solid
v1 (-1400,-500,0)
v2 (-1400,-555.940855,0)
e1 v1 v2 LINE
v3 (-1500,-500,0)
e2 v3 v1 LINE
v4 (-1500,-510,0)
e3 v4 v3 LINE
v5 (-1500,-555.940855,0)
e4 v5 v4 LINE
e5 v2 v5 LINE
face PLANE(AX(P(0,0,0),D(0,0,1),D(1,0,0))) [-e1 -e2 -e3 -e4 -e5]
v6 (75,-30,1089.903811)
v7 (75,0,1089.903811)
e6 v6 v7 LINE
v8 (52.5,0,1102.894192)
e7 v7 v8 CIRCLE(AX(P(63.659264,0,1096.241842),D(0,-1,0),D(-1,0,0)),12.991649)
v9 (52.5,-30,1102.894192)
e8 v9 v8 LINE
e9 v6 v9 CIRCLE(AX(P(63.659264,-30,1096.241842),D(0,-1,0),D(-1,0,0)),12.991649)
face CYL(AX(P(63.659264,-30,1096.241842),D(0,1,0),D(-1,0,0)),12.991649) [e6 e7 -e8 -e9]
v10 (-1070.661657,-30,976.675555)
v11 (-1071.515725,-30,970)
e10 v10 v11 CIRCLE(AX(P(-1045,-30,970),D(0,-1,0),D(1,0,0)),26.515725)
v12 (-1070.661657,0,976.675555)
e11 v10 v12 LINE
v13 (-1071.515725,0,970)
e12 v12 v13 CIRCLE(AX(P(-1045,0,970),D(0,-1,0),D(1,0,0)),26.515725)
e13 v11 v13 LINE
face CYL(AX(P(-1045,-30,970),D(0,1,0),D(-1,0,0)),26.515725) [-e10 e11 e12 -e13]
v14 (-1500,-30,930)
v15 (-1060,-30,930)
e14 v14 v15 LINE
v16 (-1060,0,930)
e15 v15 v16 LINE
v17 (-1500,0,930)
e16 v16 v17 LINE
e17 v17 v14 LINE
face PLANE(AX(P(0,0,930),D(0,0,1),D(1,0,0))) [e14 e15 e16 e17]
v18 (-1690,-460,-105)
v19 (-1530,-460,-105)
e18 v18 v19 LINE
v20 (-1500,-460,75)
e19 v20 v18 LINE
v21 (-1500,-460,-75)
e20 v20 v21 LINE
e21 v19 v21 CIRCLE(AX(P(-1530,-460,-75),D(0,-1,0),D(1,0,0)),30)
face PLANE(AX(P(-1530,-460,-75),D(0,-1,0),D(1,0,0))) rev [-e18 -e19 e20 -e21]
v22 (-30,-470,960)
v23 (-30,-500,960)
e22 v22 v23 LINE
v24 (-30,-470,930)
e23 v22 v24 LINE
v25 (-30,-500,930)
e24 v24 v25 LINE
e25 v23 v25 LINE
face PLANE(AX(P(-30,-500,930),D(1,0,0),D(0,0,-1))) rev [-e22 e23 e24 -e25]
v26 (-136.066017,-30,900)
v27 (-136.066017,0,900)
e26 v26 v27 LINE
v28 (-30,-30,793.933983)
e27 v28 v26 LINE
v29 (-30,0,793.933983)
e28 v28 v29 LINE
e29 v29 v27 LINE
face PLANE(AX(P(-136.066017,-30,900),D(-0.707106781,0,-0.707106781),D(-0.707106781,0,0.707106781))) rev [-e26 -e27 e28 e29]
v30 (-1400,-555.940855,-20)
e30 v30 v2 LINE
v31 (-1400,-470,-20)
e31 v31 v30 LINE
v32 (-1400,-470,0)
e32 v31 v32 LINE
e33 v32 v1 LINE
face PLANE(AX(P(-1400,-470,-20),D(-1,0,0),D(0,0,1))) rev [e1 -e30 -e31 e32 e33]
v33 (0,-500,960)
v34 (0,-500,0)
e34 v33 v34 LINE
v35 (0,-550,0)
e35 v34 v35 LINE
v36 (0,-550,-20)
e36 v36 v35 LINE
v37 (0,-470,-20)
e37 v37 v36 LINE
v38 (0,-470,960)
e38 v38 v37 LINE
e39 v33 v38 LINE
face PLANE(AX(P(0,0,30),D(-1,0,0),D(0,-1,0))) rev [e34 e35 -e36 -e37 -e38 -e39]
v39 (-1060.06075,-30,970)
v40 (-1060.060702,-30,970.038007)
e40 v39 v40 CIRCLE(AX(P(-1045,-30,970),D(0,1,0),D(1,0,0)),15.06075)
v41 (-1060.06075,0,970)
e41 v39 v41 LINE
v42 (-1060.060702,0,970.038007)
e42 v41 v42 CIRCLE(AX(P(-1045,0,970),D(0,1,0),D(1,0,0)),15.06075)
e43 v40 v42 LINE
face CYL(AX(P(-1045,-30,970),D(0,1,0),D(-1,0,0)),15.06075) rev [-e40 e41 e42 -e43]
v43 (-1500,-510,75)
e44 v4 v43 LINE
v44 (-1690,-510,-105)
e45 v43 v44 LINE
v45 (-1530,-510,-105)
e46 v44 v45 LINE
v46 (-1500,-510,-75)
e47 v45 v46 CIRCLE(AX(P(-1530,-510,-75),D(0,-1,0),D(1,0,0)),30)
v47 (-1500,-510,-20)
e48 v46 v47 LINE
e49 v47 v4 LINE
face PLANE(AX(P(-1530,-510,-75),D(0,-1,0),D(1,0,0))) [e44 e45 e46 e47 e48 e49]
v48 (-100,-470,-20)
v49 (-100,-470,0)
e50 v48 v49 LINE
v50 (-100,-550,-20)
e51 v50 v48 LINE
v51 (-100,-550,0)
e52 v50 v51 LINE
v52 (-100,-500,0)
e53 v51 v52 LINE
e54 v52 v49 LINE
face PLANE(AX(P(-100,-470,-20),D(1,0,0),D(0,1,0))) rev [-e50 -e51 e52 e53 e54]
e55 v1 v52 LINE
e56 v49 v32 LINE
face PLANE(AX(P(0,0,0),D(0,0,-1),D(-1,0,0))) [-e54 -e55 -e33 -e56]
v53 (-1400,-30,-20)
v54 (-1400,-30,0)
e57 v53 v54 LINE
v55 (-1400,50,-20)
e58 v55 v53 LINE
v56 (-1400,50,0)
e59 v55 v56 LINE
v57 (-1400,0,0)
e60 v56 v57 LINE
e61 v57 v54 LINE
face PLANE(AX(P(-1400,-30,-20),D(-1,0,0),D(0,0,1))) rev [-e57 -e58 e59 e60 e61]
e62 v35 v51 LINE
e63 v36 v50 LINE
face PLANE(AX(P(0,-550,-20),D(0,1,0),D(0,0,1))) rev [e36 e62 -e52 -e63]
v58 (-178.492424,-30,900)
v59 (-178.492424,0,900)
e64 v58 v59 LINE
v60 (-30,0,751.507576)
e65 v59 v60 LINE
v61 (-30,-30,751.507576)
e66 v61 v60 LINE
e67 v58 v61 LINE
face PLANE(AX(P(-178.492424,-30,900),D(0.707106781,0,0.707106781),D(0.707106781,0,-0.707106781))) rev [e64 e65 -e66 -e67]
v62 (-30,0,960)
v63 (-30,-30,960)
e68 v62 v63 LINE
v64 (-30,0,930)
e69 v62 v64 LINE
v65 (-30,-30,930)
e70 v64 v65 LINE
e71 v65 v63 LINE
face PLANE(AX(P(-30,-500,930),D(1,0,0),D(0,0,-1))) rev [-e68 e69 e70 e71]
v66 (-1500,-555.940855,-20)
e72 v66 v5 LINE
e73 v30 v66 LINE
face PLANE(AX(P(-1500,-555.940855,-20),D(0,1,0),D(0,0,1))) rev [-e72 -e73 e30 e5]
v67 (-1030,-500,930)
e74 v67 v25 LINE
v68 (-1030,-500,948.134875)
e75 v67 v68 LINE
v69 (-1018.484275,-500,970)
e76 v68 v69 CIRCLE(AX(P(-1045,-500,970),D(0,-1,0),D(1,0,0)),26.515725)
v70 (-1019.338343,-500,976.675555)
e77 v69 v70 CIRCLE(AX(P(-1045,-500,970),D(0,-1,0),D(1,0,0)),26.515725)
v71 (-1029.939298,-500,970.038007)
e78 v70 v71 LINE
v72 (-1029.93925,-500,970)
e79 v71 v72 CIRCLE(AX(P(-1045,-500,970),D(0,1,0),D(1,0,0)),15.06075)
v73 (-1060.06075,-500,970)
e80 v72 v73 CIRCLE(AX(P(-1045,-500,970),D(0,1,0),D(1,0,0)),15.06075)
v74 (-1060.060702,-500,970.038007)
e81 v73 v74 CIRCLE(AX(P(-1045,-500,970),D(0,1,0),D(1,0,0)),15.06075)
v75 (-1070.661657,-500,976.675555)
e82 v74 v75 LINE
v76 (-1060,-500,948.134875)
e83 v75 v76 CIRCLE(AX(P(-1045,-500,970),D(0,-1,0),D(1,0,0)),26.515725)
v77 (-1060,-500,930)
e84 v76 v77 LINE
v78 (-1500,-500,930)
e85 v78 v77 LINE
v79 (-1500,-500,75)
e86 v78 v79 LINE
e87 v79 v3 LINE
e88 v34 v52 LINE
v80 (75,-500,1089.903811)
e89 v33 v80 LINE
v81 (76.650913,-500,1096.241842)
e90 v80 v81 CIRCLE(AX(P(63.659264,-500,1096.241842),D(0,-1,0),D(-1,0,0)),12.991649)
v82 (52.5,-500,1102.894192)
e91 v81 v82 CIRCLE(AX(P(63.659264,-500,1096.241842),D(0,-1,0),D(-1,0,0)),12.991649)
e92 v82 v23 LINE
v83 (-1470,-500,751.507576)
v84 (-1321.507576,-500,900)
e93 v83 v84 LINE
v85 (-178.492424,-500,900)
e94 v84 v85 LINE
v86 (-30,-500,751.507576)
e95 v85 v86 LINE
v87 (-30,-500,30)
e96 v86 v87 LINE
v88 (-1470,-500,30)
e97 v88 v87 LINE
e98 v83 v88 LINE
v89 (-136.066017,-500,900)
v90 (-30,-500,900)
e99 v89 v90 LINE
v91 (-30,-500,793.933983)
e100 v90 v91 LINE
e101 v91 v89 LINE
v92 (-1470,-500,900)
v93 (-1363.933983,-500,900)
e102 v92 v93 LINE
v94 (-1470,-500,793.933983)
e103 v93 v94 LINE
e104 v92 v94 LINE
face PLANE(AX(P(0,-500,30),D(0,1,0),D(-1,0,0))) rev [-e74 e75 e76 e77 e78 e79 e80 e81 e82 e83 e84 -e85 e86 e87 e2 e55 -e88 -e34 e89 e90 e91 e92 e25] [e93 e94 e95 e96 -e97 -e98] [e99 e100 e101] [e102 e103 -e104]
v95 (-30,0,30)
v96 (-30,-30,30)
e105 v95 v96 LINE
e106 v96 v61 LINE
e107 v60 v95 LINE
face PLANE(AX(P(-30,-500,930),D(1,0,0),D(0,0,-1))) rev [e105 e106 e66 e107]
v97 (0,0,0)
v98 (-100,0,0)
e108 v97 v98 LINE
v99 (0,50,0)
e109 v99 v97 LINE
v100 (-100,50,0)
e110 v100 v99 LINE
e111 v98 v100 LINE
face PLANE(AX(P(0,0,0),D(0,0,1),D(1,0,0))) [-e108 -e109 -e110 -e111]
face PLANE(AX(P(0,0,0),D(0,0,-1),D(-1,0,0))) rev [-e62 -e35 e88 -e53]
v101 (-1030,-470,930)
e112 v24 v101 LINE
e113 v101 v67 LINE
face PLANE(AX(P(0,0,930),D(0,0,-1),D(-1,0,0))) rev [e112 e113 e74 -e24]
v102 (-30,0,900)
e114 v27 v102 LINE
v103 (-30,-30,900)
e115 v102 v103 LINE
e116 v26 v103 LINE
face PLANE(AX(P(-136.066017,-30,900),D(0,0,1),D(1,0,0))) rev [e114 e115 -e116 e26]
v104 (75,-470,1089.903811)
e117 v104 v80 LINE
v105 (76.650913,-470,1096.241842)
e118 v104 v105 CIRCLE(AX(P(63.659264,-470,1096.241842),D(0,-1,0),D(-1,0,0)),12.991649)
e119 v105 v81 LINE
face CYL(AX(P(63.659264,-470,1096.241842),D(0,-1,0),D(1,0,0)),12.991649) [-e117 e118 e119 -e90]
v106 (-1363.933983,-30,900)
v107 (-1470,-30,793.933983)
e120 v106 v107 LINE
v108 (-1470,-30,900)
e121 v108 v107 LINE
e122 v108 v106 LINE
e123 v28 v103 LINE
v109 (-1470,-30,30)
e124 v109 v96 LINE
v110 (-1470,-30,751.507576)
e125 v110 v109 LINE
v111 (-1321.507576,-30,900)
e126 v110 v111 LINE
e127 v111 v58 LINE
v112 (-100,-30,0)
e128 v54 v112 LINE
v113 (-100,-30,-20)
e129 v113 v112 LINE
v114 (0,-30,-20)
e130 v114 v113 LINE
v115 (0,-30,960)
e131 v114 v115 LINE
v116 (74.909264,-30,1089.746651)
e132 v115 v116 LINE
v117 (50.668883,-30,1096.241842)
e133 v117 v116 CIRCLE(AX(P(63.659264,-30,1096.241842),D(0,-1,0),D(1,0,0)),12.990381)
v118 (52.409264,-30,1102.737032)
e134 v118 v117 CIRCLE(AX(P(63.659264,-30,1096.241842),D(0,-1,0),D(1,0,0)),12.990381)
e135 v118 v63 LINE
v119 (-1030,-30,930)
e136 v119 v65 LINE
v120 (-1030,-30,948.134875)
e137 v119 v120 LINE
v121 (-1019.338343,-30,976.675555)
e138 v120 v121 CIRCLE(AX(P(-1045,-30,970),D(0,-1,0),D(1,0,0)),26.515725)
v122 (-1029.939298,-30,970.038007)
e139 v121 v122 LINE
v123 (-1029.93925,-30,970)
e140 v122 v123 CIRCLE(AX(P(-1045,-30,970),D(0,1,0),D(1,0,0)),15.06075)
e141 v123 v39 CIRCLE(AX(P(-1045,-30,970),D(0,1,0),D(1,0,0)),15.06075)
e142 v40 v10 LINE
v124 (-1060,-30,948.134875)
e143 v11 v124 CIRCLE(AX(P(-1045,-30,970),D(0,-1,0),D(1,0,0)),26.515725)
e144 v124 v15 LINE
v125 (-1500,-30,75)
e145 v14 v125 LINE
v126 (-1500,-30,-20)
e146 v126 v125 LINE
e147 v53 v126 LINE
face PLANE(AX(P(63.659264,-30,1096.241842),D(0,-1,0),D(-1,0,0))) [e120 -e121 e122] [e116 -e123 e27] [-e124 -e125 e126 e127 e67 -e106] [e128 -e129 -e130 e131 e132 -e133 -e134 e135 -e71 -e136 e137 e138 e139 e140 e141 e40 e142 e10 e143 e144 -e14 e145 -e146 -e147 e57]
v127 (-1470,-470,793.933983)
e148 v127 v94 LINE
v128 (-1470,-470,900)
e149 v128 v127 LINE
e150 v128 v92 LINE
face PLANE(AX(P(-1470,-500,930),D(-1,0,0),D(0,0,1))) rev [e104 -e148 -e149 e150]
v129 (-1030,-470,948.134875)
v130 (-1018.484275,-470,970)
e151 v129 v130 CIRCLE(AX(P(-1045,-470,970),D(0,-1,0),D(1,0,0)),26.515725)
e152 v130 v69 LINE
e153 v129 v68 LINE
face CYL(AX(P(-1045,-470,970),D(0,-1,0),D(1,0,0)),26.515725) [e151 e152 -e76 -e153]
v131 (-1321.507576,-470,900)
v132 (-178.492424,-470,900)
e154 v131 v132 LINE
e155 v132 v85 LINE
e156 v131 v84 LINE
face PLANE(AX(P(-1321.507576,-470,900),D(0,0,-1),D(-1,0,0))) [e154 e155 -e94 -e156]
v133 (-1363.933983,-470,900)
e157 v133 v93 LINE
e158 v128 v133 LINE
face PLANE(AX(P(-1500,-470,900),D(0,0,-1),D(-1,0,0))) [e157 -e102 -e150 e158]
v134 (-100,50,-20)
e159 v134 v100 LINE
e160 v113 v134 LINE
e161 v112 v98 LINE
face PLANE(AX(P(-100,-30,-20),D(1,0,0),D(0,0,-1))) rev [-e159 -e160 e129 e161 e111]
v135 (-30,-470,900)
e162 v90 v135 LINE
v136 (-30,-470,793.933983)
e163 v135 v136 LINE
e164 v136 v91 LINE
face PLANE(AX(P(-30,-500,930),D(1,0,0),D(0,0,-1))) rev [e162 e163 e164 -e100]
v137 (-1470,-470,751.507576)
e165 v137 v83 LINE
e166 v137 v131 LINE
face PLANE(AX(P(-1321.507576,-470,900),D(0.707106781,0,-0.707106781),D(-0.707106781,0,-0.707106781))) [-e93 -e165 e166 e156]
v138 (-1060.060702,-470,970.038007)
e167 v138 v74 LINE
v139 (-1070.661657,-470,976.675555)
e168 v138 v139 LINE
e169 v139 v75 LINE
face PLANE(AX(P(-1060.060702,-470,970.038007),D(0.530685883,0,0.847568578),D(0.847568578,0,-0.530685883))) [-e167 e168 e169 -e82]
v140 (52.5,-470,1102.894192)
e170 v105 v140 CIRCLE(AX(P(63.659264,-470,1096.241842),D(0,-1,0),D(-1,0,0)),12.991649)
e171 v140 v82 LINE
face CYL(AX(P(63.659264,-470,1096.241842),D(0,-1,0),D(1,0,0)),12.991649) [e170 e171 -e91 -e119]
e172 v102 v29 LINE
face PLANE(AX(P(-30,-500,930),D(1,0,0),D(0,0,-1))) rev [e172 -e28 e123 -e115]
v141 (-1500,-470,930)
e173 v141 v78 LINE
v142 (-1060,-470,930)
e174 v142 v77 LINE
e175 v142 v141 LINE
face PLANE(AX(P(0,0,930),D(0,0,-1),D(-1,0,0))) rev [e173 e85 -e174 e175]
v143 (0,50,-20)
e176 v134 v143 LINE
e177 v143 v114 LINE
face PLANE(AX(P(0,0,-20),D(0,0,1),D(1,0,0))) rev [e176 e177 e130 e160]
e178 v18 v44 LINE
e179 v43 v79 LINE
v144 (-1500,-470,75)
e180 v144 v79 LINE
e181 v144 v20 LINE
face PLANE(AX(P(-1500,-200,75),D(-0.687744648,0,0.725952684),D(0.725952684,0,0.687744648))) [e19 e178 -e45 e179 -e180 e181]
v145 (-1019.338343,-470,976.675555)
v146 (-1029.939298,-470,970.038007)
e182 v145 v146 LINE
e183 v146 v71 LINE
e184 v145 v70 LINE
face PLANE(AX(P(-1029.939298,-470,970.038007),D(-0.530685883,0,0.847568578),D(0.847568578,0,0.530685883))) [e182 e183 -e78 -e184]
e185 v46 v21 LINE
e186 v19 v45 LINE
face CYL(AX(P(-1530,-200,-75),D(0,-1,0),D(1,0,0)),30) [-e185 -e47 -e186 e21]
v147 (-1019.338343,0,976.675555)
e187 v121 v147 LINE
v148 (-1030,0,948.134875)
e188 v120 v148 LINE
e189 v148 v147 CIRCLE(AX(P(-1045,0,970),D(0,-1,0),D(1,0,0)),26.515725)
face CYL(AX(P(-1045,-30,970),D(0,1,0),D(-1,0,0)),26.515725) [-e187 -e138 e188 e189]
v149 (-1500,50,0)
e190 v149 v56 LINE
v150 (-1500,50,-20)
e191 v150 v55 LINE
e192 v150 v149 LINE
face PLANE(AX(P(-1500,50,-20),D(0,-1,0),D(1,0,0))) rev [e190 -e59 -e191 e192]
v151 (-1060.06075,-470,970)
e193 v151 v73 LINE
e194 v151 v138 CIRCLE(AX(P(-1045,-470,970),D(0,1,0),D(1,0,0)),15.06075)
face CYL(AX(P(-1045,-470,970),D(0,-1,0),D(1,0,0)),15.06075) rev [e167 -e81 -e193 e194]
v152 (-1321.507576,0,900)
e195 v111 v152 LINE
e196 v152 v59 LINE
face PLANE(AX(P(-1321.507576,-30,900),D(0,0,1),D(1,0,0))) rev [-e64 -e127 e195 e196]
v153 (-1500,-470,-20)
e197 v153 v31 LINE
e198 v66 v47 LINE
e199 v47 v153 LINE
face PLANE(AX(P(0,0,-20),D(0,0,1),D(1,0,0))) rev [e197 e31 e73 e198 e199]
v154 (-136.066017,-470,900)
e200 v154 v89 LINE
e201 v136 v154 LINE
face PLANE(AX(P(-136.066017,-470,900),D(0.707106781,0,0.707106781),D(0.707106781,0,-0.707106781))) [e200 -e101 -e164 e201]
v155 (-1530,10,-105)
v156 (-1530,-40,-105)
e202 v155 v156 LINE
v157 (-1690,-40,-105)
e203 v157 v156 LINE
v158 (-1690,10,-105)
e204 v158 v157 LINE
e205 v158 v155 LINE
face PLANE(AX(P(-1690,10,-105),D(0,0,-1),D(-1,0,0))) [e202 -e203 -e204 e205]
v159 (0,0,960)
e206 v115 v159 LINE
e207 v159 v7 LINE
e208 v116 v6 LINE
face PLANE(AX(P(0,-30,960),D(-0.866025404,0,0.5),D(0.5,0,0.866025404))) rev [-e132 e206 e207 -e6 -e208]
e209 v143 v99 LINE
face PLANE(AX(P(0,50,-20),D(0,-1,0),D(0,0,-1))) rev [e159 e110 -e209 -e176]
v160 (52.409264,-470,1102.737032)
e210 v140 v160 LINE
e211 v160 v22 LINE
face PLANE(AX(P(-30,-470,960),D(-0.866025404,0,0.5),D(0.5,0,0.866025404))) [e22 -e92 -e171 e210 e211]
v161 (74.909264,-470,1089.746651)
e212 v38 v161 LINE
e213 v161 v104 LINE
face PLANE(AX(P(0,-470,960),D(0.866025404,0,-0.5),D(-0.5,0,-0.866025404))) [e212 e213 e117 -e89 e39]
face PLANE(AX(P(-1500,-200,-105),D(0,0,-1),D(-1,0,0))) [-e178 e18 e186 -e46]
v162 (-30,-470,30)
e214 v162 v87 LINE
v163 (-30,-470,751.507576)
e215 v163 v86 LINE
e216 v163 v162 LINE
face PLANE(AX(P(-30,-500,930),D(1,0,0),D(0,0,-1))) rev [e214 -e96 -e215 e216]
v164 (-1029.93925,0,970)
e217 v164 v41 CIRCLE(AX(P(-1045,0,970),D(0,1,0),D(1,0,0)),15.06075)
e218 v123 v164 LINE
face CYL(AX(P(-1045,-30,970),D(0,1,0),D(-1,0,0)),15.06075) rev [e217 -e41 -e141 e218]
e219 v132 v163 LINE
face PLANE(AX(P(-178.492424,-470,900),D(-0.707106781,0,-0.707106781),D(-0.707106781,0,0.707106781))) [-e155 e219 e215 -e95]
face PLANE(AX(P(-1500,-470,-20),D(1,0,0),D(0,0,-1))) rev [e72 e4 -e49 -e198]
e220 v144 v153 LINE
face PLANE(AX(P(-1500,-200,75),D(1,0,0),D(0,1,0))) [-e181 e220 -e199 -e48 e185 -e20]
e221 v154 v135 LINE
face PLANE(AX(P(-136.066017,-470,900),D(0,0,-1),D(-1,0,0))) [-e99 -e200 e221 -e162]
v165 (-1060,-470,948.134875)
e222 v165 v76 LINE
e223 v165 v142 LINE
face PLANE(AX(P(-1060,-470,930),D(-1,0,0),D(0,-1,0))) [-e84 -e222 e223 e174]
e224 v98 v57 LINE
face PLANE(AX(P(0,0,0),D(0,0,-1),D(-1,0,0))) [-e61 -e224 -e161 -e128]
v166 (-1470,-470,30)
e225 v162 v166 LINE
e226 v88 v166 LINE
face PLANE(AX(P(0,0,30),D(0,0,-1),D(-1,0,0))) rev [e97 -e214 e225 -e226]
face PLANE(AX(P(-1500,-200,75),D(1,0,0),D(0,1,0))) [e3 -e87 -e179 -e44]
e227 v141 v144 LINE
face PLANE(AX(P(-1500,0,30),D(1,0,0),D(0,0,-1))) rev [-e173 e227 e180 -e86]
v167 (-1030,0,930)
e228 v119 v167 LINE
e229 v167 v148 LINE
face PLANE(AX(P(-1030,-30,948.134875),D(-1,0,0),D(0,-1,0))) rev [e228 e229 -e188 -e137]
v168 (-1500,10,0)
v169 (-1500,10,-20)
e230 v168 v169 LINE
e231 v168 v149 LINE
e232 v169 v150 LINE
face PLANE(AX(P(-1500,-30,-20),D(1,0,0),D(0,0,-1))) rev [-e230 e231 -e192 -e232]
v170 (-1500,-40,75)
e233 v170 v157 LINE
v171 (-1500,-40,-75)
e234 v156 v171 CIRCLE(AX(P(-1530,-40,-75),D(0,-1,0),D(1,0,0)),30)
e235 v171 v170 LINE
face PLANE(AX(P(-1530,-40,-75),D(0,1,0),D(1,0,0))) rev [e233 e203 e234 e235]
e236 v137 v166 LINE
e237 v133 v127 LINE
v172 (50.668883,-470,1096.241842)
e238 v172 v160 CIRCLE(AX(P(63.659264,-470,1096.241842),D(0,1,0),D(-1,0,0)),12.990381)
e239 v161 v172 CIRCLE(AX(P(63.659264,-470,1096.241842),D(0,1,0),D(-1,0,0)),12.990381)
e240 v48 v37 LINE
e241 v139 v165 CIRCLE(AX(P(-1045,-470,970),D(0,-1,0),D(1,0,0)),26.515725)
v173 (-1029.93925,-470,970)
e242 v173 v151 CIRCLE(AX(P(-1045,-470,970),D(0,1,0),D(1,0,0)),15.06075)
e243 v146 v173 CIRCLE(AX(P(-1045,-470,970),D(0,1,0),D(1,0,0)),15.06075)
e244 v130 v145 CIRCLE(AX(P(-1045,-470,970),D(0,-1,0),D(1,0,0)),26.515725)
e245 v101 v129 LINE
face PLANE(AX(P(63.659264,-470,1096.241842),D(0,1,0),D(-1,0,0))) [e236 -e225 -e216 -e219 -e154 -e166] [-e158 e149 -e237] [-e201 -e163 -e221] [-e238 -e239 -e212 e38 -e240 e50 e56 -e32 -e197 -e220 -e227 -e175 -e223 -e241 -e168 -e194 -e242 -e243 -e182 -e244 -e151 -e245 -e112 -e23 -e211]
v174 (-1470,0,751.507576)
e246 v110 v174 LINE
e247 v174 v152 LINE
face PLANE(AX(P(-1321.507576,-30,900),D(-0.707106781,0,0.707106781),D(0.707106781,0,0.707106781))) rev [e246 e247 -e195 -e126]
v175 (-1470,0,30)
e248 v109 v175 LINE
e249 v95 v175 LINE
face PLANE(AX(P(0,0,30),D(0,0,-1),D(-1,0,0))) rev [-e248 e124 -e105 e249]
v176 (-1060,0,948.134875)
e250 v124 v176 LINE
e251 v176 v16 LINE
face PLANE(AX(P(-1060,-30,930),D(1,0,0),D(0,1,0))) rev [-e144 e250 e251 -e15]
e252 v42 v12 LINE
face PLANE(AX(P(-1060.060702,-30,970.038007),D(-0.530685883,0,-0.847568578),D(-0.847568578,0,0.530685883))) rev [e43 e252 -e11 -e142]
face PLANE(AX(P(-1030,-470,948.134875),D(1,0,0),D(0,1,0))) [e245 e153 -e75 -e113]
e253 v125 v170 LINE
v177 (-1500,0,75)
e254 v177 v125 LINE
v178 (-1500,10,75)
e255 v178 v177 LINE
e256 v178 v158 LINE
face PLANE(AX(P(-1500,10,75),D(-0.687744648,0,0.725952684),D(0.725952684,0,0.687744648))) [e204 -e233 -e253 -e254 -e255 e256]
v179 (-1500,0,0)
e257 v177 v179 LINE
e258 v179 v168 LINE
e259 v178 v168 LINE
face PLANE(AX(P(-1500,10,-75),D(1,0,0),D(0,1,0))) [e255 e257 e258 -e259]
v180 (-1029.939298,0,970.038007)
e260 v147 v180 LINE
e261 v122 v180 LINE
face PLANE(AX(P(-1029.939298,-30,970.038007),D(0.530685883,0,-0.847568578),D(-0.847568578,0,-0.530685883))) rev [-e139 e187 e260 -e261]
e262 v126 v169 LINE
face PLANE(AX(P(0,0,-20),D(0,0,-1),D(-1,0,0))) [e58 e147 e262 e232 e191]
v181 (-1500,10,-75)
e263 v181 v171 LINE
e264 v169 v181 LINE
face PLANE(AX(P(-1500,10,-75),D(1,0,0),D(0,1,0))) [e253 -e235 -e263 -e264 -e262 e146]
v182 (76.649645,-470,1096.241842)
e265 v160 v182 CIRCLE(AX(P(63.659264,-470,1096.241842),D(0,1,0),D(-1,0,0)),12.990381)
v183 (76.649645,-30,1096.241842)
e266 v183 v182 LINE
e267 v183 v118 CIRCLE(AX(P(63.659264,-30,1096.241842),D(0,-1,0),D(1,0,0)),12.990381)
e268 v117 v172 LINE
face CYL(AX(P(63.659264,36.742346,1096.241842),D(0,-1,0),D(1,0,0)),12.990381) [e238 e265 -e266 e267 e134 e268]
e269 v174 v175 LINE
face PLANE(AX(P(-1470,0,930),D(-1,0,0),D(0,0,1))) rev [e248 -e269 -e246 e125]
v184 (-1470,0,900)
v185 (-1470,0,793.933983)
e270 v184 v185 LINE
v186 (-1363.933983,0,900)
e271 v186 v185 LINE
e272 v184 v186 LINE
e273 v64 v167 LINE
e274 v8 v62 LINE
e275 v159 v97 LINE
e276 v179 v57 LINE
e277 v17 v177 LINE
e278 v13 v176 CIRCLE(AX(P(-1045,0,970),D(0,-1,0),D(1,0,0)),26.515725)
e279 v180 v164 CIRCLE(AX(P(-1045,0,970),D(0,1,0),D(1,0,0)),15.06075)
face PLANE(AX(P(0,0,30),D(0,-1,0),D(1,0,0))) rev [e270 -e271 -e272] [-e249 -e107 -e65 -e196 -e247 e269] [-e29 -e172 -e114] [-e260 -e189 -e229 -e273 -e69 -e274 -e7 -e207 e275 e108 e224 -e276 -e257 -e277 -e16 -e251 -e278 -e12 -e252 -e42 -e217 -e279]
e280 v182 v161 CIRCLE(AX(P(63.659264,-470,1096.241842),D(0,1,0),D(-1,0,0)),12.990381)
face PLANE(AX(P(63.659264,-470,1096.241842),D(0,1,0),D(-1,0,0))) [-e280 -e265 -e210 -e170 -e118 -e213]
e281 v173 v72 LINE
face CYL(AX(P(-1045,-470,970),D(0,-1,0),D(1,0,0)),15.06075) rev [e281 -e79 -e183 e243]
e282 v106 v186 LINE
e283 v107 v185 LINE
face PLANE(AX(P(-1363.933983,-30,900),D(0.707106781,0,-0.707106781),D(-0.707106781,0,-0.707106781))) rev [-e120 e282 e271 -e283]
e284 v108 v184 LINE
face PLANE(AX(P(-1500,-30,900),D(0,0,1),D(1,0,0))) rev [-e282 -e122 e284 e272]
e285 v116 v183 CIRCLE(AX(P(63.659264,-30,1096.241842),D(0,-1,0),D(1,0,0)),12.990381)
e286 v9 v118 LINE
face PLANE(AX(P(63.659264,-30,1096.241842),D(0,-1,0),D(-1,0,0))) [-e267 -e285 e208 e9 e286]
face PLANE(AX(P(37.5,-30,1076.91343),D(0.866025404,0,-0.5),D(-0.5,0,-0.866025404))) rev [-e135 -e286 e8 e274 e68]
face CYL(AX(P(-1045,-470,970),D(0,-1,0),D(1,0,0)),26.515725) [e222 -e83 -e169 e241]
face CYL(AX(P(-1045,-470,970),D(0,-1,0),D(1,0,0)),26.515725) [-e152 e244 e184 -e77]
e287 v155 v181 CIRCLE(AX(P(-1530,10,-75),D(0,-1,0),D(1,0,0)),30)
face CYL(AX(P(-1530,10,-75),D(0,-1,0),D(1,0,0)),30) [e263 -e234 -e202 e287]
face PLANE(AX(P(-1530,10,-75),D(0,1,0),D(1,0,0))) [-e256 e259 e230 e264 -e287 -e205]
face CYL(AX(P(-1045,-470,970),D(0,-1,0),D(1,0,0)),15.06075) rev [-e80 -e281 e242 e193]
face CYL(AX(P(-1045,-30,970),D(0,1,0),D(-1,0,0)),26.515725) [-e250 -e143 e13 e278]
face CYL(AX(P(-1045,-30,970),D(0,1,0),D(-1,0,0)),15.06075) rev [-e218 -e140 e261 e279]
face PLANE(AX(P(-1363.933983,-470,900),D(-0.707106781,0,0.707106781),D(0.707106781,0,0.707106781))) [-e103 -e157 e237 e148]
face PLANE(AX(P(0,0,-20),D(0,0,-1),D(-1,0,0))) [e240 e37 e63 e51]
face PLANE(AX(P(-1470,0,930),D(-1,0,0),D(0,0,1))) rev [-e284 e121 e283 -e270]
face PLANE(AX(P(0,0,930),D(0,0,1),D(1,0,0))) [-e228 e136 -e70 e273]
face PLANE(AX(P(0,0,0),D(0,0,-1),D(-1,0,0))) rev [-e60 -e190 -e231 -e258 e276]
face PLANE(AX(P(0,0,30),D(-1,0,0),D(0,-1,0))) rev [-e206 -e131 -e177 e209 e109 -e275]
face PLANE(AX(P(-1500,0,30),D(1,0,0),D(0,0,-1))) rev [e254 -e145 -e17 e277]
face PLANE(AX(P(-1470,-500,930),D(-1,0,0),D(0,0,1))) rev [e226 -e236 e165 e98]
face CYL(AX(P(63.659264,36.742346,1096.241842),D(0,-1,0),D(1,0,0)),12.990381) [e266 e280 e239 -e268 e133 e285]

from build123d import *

# Parameters (mm, degrees)
SKETCH1_W            = 1500
SKETCH1_H            = 500
BOSS_EXTRUDE1_DEPTH  = 30
SKETCH2_W            = 30
SKETCH2_H            = 30
BOSS_EXTRUDE2_DEPTH  = 900
BOSS_EXTRUDE3_DEPTH  = 30
SKETCH4_W            = 30
SKETCH4_H            = 500
BOSS_EXTRUDE4_DEPTH  = 30
BOSS_EXTRUDE5_DEPTH  = 30
SKETCH6_R            = 12.990381057
BOSS_EXTRUDE6_DEPTH  = 500
BOSS_EXTRUDE7_DEPTH  = 30
BOSS_EXTRUDE8_DEPTH  = 300
FILLET1_R            = 30
SKETCH11_W           = 960
SKETCH11_H           = 500
BOSS_EXTRUDE9_DEPTH  = 30
SKETCH12_W           = 40
SKETCH12_H           = 220
CUT_EXTRUDE1_DEPTH   = 300
SKETCH13_W           = 1153.001247693
SKETCH13_H           = 440
CUT_EXTRUDE2_DEPTH   = 2083.426213795
BOSS_EXTRUDE11_DEPTH = 25
SKETCH16_W           = 100
SKETCH16_H           = 80
SKETCH16_H_2         = 85.940855112
BOSS_EXTRUDE12_DEPTH = 20


with BuildPart() as part:
    # Sketch1 → Boss-Extrude1 (new body)
    with BuildSketch(Plane.XY):
        with Locations((-750, -250)):
            Rectangle(SKETCH1_W, SKETCH1_H)
    extrude(amount=BOSS_EXTRUDE1_DEPTH)

    # Sketch2 → Boss-Extrude2 (add)
    with BuildSketch(Plane.XY.offset(30)):
        with Locations((-1485, -485)):
            Rectangle(SKETCH2_W, SKETCH2_H)
        with Locations((-1485, -15)):
            Rectangle(SKETCH2_W, SKETCH2_H)
        with Locations((-15, -15)):
            Rectangle(SKETCH2_W, SKETCH2_H)
        with Locations((-15, -485)):
            Rectangle(SKETCH2_W, SKETCH2_H)
    extrude(amount=BOSS_EXTRUDE2_DEPTH)

    # Sketch3 → Boss-Extrude3 (add)
    with BuildSketch(Plane.XZ.offset(500)):
        Polygon((-1500, 930), (0, 930), (0, 900), (-136.066017178, 900), (-30, 793.933982822), (-30, 751.507575951), (-178.492424049, 900), (-1321.507575951, 900), (-1470, 751.507575951), (-1470, 793.933982822), (-1363.933982822, 900), (-1500, 900), align=None)
    boss_extrude3 = extrude(amount=-BOSS_EXTRUDE3_DEPTH)

    # Mirror2: Boss-Extrude3 across plane
    add(boss_extrude3.mirror(Plane.ZX.offset(-250)))

    # Sketch4 → Boss-Extrude4 (add)
    with BuildSketch(Plane.XY.offset(930)):
        with Locations((-15, -250)):
            Rectangle(SKETCH4_W, SKETCH4_H)
    extrude(amount=BOSS_EXTRUDE4_DEPTH)

    # Sketch5 → Boss-Extrude5 (add)
    with BuildSketch(Plane.XZ.offset(500)):
        with BuildLine():
            Line((0, 960), (75, 1089.903810568))
            ThreePointArc((75, 1089.903810568), (70.155088258, 1107.492939386), (52.5, 1102.894191624))
            Line((52.5, 1102.894191624), (37.5, 1076.913429511))
            Line((37.5, 1076.913429511), (30.236347458, 1064.33241426))
            Line((30.236347458, 1064.33241426), (-30, 960))
            Line((-30, 960), (0, 960))
        make_face()
    boss_extrude5 = extrude(amount=-BOSS_EXTRUDE5_DEPTH)

    # Mirror3: Boss-Extrude5 across plane
    add(boss_extrude5.mirror(Plane.ZX.offset(-250)))

    # Sketch6 → Boss-Extrude6 (add)
    with BuildSketch(Plane.XZ.offset(500)):
        with Locations(Location((63.659263982, 1096.241841703, 0), (0, 0, 330))):
            Circle(SKETCH6_R)
    extrude(amount=-BOSS_EXTRUDE6_DEPTH)

    # Sketch8 → Boss-Extrude7 (add)
    with BuildSketch(Plane.XZ.offset(500)):
        with BuildLine():
            Line((-1060, 930), (-1030, 930))
            Line((-1030, 930), (-1030, 948.134875189))
            ThreePointArc((-1030, 948.134875189), (-1020.16081333, 960.721072878), (-1019.338342911, 976.675555288))
            Line((-1019.338342911, 976.675555288), (-1029.939297882, 970.038007257))
            ThreePointArc((-1029.939297882, 970.038007257), (-1045, 954.939249924), (-1060.060702118, 970.038007257))
            Line((-1060.060702118, 970.038007257), (-1070.661657089, 976.675555288))
            ThreePointArc((-1070.661657089, 976.675555288), (-1069.83918667, 960.721072878), (-1060, 948.134875189))
            Line((-1060, 948.134875189), (-1060, 930))
        make_face()
    boss_extrude7 = extrude(amount=-BOSS_EXTRUDE7_DEPTH)

    # Mirror4: Boss-Extrude7 across plane
    add(boss_extrude7.mirror(Plane.ZX.offset(-250)))

    # Sketch10 → Boss-Extrude8 (add)
    with BuildSketch(Plane.XZ.offset(500)):
        Polygon((-1500, 75), (-1500, -105), (-1690, -105), align=None)
    extrude(amount=-BOSS_EXTRUDE8_DEPTH)

    # Fillet1
    fillet1_edges = [part.edges().sort_by_distance(p)[0] for p in [
        (-1500, -350, -105),
    ]]
    fillet(fillet1_edges, radius=FILLET1_R)

    # Sketch11 → Boss-Extrude9 (add)
    with BuildSketch(Plane(origin=(0, 0, 0), x_dir=(0, 0, -1), z_dir=(1, 0, 0))):
        with Locations((-480, -250)):
            Rectangle(SKETCH11_W, SKETCH11_H)
    extrude(amount=-BOSS_EXTRUDE9_DEPTH)

    # Sketch12 → Cut-Extrude1 (cut)
    with BuildSketch(Plane(origin=(0, 0, 0), x_dir=(0, 0, -1), z_dir=(1, 0, 0))):
        with Locations((-70, -350)):
            Rectangle(SKETCH12_W, SKETCH12_H)
    extrude(amount=-CUT_EXTRUDE1_DEPTH, mode=Mode.SUBTRACT)

    # Sketch13 → Cut-Extrude2 (cut, through all)
    with BuildSketch(Plane(origin=(0, 0, 0), x_dir=(0, 0, -1), z_dir=(1, 0, 0))):
        with Locations((-383.499376154, -250)):
            Rectangle(SKETCH13_W, SKETCH13_H)
    extrude(amount=-CUT_EXTRUDE2_DEPTH, mode=Mode.SUBTRACT)

    # Sketch15 → Boss-Extrude11 (add, symmetric)
    with BuildSketch(Plane(origin=(0, -485, 0), x_dir=(-1, 0, 0), z_dir=(0, -1, 0))):
        with BuildLine():
            Line((1500, -75), (1500, 0))
            Line((1500, 0), (1500, 75))
            ThreePointArc((1500, 75), (1508.786796564, 96.213203436), (1530, 105))
            Line((1530, 105), (1690, 105))
            Line((1690, 105), (1500, -75))
        make_face()
    boss_extrude11 = extrude(amount=BOSS_EXTRUDE11_DEPTH, both=True)

    # Mirror5: Boss-Extrude11 across plane
    add(boss_extrude11.mirror(Plane.ZX.offset(-250)))

    # Sketch16 → Boss-Extrude12 (add)
    with BuildSketch(Plane(origin=(0, 0, 0), x_dir=(-1, 0, 0), z_dir=(0, 0, -1))):
        with Locations((1450, 10)):
            Rectangle(SKETCH16_W, SKETCH16_H)
        with Locations((1450, -512.970427556)):
            Rectangle(SKETCH16_W, SKETCH16_H_2)
        with Locations((50, -510)):
            Rectangle(SKETCH16_W, SKETCH16_H)
        with Locations((50, 10)):
            Rectangle(SKETCH16_W, SKETCH16_H)
    extrude(amount=BOSS_EXTRUDE12_DEPTH)


solid = part.part
